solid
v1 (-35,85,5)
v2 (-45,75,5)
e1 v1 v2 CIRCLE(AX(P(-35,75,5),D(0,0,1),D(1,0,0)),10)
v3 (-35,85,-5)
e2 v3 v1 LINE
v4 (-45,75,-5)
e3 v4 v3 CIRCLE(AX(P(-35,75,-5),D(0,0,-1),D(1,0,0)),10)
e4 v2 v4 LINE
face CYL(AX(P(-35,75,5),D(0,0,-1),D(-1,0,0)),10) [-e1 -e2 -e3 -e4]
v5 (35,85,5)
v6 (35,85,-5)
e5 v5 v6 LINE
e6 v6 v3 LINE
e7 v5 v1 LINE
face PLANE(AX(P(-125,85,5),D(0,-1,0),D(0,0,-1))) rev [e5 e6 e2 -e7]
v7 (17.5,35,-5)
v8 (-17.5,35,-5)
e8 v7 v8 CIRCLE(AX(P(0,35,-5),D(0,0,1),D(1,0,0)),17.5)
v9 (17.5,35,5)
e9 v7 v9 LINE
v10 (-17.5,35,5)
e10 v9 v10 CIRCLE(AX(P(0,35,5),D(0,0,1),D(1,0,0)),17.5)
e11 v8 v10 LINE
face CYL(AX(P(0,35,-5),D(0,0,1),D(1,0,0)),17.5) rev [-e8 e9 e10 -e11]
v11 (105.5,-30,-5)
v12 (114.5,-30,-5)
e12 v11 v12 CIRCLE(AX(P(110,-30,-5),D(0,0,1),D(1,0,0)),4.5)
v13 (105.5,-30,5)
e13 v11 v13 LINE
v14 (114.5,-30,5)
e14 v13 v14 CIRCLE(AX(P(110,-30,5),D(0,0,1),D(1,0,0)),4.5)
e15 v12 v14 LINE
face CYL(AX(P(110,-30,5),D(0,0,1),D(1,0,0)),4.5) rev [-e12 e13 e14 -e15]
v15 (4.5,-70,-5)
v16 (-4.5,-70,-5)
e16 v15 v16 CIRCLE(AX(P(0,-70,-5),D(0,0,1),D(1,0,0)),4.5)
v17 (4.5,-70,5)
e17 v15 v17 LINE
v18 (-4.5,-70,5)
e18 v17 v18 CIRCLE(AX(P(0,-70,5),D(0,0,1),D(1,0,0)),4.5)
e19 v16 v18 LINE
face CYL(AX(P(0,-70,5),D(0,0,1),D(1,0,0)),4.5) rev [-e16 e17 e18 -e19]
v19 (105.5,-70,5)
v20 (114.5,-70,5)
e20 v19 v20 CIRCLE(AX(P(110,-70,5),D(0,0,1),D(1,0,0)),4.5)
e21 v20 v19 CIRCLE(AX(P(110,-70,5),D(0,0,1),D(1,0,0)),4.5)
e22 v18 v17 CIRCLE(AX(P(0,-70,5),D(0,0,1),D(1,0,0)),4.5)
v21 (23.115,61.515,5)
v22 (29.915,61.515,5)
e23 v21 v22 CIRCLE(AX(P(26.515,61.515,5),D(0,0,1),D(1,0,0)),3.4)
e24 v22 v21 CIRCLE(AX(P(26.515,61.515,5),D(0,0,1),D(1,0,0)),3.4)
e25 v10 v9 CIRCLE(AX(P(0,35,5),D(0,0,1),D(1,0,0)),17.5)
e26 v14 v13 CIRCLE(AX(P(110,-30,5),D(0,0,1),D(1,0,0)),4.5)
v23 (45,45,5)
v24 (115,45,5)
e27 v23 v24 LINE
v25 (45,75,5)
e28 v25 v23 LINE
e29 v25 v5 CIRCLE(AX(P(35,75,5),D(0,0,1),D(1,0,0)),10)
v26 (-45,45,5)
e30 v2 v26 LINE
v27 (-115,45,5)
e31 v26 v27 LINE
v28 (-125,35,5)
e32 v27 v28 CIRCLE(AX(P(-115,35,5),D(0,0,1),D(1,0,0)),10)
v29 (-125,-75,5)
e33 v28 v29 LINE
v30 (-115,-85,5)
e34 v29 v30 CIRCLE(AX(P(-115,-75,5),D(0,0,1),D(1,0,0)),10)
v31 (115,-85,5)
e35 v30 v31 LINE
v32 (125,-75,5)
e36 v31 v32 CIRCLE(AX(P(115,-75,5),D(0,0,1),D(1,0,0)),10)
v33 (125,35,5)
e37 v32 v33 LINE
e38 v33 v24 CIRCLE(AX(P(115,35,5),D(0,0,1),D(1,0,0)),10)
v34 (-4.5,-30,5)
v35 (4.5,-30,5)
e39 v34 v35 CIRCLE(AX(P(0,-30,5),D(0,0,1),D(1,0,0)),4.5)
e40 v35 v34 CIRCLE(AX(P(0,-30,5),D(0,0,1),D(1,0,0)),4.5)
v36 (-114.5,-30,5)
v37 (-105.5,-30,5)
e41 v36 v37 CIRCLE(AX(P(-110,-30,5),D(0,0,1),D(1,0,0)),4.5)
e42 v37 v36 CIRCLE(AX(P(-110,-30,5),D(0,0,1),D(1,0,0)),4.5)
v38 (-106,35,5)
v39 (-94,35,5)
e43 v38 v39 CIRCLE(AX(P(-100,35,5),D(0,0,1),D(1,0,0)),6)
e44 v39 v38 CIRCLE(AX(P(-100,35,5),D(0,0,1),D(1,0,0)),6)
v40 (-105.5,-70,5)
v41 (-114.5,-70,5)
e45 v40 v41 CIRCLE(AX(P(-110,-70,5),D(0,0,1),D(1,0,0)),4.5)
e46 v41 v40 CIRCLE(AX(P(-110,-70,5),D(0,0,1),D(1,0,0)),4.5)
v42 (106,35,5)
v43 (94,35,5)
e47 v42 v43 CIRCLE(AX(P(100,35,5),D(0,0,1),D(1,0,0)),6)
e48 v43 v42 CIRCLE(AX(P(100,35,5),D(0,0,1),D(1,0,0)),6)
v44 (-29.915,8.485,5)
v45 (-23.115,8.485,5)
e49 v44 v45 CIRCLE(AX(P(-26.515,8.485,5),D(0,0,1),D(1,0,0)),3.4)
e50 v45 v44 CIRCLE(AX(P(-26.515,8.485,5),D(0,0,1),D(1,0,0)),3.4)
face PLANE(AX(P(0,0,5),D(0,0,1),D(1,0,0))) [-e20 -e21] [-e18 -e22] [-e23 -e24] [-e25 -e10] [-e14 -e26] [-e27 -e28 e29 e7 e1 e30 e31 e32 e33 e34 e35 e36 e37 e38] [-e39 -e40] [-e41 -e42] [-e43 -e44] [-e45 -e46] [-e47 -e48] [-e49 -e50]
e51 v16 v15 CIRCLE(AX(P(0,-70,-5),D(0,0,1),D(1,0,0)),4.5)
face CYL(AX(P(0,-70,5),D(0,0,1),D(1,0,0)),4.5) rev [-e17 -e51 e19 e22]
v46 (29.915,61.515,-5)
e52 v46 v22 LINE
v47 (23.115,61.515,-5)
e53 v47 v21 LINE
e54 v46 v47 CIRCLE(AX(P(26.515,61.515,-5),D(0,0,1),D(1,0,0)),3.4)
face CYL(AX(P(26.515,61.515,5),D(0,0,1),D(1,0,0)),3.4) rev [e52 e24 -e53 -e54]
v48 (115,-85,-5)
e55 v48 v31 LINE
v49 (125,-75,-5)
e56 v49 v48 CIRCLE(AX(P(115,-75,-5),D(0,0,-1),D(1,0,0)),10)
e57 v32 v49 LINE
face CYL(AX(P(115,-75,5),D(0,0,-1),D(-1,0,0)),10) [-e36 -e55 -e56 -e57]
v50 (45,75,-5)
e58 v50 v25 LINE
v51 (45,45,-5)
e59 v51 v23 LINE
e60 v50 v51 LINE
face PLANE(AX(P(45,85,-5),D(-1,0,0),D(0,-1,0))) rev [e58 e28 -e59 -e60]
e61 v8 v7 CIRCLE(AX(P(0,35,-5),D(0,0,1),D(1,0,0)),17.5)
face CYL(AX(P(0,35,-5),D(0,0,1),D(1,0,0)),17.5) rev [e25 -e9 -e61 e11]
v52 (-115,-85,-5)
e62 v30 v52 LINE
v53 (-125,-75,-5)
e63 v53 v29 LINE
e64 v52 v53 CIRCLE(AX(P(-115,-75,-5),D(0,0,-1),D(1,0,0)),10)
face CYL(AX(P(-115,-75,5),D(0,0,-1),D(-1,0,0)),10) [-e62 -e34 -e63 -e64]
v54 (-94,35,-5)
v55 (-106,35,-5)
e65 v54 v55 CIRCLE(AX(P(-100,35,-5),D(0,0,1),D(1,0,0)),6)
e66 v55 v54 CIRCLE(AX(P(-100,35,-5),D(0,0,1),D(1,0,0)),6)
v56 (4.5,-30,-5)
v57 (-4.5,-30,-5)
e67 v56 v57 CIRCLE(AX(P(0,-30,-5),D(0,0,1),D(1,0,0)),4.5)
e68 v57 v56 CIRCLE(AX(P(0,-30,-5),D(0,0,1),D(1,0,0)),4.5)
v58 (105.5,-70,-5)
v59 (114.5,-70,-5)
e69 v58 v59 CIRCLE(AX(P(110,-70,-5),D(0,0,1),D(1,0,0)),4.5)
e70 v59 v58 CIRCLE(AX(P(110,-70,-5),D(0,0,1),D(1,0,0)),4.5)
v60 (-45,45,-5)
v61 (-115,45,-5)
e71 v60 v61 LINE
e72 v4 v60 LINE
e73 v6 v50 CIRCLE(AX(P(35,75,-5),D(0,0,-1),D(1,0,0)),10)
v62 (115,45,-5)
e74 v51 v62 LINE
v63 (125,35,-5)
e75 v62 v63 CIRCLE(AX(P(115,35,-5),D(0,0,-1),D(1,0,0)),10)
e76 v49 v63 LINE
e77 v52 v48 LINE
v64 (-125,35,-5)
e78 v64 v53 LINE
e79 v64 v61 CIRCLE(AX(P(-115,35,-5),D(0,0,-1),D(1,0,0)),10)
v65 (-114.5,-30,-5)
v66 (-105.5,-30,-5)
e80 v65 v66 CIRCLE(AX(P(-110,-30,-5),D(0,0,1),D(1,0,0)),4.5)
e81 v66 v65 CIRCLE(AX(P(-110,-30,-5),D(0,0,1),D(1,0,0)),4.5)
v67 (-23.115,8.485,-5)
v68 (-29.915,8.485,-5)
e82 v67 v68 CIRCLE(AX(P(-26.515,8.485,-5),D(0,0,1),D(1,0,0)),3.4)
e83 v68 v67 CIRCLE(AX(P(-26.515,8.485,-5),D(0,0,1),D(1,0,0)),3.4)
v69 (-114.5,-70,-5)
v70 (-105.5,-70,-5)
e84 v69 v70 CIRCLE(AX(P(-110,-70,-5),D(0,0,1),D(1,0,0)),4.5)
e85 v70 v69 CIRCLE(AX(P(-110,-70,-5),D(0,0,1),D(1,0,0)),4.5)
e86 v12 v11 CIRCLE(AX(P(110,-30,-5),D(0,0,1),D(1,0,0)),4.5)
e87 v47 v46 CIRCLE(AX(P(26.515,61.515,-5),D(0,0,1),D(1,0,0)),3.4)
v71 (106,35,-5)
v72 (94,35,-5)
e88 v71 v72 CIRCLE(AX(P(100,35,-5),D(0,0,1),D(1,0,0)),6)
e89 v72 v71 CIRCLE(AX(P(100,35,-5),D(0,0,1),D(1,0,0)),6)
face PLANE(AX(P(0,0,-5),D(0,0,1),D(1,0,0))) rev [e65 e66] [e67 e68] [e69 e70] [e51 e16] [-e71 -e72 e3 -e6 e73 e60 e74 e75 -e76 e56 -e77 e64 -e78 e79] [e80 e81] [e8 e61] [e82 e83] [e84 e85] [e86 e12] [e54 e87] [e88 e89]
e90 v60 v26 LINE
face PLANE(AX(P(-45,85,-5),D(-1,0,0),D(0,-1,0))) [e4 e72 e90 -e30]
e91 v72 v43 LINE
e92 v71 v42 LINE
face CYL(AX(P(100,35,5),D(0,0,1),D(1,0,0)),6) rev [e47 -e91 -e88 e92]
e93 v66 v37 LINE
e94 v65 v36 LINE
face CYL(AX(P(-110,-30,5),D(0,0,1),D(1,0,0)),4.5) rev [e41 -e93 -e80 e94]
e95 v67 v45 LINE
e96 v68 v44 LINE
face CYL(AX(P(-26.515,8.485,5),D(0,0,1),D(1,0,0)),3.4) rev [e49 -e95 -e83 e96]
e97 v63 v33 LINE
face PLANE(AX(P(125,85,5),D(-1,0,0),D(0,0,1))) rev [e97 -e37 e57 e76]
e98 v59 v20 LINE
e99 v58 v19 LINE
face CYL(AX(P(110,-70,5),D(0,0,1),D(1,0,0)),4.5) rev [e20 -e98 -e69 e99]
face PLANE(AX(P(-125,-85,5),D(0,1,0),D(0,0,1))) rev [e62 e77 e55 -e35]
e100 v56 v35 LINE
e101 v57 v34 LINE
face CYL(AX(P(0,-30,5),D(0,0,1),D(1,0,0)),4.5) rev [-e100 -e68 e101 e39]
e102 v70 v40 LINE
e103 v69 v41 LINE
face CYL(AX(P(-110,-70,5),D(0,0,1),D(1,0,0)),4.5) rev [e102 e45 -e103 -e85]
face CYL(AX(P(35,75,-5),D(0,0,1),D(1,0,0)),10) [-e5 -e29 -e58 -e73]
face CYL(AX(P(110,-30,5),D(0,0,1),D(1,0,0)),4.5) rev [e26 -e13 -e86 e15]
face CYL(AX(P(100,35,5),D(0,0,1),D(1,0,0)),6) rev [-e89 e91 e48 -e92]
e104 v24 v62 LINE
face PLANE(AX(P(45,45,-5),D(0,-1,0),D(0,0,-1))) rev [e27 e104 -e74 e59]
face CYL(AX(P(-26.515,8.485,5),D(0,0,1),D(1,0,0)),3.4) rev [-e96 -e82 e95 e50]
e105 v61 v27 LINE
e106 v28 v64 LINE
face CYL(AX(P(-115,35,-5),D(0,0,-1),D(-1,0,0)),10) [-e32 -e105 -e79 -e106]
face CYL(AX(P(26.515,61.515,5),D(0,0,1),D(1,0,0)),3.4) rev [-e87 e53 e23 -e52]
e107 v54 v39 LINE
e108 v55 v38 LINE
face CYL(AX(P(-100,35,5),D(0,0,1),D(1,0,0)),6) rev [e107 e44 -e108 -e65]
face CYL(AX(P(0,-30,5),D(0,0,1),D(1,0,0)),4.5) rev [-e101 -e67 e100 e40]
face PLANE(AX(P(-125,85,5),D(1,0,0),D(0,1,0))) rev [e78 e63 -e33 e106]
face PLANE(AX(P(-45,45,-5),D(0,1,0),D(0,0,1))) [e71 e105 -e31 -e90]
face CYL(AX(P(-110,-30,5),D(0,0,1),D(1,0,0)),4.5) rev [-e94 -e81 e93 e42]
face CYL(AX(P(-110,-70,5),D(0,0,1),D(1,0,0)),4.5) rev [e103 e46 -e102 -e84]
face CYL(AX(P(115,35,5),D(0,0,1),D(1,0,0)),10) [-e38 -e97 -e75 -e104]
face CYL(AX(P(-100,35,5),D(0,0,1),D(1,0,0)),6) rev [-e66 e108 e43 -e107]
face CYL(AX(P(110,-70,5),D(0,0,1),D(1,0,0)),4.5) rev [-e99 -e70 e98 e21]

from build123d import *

# Parameters (mm, degrees)
SKETCH_1_W              = 250
SKETCH_1_H              = 170
EXTRUDE_1_DEPTH         = 5
SKETCH_2_W              = 80
SKETCH_2_H              = 40
CUT_EXTRUDE_1_DEPTH     = 10
HOLE_WIZARD_9_0_9_1_D   = 9
PATTERN_LINEAR_1_COUNT  = 3
PATTERN_LINEAR_1_PITCH  = 110
HOLE_WIZARD_12_0_12_1_D = 12
SKETCH_7_R              = 17.5
CUT_EXTRUDE_2_DEPTH     = 10
HOLE_WIZARD_M8_1_D      = 6.8
FILLET_1_R              = 10


with BuildPart() as part:
    # 草图1 → 凸台-拉伸1 (new, symmetric)
    with BuildSketch(Plane.XY):
        Rectangle(SKETCH_1_W, SKETCH_1_H)
    extrude(amount=EXTRUDE_1_DEPTH, both=True)

    # 草图2 → 切除-拉伸1 (cut)
    with BuildSketch(Plane.XY.offset(5)):
        with Locations((85, 65)):
            Rectangle(SKETCH_2_W, SKETCH_2_H)
    cut_extrude_1 = extrude(amount=-CUT_EXTRUDE_1_DEPTH, mode=Mode.SUBTRACT)

    # 镜向1: 切除-拉伸1 across plane
    add(cut_extrude_1.mirror(Plane(origin=(0, 0, 0), x_dir=(0, 0, 1), z_dir=(1, 0, 0))), mode=Mode.SUBTRACT)

    # Ø9.0 (9) 直径孔1 (through all)
    with Locations(Plane.XY.offset(5)):
        with Locations((-110, -30), (-110, -70)):
            hole_wizard_9_0_9_1 = Hole(HOLE_WIZARD_9_0_9_1_D / 2)

    # 阵列(线性)1: Ø9.0 (9) 直径孔1 ×3
    with Locations(*[(i * PATTERN_LINEAR_1_PITCH, 0, 0) for i in range(1, PATTERN_LINEAR_1_COUNT)]):
        add(hole_wizard_9_0_9_1, mode=Mode.SUBTRACT)

    # Ø12.0 (12) 直径孔1 (through all)
    with Locations(Plane.XY.offset(5)):
        with Locations((-100, 35), (100, 35)):
            Hole(HOLE_WIZARD_12_0_12_1_D / 2)

    # 草图7 → 切除-拉伸2 (cut)
    with BuildSketch(Plane.XY.offset(5)):
        with Locations((0, 35)):
            Circle(SKETCH_7_R)
    extrude(amount=-CUT_EXTRUDE_2_DEPTH, mode=Mode.SUBTRACT)

    # M8 螺纹孔1 (through all)
    with Locations(Plane.XY.offset(5)):
        with Locations((-26.515, 8.485), (26.515, 61.515)):
            Hole(HOLE_WIZARD_M8_1_D / 2)

    # 圆角1
    fillet_1_edges = [part.edges().sort_by_distance(p)[0] for p in [
        (45, 85, 0),
        (125, 45, 0),
        (-45, 85, 0),
        (-125, 45, 0),
        (125, -85, 0),
        (-125, -85, 0),
    ]]
    fillet(fillet_1_edges, radius=FILLET_1_R)


solid = part.part
